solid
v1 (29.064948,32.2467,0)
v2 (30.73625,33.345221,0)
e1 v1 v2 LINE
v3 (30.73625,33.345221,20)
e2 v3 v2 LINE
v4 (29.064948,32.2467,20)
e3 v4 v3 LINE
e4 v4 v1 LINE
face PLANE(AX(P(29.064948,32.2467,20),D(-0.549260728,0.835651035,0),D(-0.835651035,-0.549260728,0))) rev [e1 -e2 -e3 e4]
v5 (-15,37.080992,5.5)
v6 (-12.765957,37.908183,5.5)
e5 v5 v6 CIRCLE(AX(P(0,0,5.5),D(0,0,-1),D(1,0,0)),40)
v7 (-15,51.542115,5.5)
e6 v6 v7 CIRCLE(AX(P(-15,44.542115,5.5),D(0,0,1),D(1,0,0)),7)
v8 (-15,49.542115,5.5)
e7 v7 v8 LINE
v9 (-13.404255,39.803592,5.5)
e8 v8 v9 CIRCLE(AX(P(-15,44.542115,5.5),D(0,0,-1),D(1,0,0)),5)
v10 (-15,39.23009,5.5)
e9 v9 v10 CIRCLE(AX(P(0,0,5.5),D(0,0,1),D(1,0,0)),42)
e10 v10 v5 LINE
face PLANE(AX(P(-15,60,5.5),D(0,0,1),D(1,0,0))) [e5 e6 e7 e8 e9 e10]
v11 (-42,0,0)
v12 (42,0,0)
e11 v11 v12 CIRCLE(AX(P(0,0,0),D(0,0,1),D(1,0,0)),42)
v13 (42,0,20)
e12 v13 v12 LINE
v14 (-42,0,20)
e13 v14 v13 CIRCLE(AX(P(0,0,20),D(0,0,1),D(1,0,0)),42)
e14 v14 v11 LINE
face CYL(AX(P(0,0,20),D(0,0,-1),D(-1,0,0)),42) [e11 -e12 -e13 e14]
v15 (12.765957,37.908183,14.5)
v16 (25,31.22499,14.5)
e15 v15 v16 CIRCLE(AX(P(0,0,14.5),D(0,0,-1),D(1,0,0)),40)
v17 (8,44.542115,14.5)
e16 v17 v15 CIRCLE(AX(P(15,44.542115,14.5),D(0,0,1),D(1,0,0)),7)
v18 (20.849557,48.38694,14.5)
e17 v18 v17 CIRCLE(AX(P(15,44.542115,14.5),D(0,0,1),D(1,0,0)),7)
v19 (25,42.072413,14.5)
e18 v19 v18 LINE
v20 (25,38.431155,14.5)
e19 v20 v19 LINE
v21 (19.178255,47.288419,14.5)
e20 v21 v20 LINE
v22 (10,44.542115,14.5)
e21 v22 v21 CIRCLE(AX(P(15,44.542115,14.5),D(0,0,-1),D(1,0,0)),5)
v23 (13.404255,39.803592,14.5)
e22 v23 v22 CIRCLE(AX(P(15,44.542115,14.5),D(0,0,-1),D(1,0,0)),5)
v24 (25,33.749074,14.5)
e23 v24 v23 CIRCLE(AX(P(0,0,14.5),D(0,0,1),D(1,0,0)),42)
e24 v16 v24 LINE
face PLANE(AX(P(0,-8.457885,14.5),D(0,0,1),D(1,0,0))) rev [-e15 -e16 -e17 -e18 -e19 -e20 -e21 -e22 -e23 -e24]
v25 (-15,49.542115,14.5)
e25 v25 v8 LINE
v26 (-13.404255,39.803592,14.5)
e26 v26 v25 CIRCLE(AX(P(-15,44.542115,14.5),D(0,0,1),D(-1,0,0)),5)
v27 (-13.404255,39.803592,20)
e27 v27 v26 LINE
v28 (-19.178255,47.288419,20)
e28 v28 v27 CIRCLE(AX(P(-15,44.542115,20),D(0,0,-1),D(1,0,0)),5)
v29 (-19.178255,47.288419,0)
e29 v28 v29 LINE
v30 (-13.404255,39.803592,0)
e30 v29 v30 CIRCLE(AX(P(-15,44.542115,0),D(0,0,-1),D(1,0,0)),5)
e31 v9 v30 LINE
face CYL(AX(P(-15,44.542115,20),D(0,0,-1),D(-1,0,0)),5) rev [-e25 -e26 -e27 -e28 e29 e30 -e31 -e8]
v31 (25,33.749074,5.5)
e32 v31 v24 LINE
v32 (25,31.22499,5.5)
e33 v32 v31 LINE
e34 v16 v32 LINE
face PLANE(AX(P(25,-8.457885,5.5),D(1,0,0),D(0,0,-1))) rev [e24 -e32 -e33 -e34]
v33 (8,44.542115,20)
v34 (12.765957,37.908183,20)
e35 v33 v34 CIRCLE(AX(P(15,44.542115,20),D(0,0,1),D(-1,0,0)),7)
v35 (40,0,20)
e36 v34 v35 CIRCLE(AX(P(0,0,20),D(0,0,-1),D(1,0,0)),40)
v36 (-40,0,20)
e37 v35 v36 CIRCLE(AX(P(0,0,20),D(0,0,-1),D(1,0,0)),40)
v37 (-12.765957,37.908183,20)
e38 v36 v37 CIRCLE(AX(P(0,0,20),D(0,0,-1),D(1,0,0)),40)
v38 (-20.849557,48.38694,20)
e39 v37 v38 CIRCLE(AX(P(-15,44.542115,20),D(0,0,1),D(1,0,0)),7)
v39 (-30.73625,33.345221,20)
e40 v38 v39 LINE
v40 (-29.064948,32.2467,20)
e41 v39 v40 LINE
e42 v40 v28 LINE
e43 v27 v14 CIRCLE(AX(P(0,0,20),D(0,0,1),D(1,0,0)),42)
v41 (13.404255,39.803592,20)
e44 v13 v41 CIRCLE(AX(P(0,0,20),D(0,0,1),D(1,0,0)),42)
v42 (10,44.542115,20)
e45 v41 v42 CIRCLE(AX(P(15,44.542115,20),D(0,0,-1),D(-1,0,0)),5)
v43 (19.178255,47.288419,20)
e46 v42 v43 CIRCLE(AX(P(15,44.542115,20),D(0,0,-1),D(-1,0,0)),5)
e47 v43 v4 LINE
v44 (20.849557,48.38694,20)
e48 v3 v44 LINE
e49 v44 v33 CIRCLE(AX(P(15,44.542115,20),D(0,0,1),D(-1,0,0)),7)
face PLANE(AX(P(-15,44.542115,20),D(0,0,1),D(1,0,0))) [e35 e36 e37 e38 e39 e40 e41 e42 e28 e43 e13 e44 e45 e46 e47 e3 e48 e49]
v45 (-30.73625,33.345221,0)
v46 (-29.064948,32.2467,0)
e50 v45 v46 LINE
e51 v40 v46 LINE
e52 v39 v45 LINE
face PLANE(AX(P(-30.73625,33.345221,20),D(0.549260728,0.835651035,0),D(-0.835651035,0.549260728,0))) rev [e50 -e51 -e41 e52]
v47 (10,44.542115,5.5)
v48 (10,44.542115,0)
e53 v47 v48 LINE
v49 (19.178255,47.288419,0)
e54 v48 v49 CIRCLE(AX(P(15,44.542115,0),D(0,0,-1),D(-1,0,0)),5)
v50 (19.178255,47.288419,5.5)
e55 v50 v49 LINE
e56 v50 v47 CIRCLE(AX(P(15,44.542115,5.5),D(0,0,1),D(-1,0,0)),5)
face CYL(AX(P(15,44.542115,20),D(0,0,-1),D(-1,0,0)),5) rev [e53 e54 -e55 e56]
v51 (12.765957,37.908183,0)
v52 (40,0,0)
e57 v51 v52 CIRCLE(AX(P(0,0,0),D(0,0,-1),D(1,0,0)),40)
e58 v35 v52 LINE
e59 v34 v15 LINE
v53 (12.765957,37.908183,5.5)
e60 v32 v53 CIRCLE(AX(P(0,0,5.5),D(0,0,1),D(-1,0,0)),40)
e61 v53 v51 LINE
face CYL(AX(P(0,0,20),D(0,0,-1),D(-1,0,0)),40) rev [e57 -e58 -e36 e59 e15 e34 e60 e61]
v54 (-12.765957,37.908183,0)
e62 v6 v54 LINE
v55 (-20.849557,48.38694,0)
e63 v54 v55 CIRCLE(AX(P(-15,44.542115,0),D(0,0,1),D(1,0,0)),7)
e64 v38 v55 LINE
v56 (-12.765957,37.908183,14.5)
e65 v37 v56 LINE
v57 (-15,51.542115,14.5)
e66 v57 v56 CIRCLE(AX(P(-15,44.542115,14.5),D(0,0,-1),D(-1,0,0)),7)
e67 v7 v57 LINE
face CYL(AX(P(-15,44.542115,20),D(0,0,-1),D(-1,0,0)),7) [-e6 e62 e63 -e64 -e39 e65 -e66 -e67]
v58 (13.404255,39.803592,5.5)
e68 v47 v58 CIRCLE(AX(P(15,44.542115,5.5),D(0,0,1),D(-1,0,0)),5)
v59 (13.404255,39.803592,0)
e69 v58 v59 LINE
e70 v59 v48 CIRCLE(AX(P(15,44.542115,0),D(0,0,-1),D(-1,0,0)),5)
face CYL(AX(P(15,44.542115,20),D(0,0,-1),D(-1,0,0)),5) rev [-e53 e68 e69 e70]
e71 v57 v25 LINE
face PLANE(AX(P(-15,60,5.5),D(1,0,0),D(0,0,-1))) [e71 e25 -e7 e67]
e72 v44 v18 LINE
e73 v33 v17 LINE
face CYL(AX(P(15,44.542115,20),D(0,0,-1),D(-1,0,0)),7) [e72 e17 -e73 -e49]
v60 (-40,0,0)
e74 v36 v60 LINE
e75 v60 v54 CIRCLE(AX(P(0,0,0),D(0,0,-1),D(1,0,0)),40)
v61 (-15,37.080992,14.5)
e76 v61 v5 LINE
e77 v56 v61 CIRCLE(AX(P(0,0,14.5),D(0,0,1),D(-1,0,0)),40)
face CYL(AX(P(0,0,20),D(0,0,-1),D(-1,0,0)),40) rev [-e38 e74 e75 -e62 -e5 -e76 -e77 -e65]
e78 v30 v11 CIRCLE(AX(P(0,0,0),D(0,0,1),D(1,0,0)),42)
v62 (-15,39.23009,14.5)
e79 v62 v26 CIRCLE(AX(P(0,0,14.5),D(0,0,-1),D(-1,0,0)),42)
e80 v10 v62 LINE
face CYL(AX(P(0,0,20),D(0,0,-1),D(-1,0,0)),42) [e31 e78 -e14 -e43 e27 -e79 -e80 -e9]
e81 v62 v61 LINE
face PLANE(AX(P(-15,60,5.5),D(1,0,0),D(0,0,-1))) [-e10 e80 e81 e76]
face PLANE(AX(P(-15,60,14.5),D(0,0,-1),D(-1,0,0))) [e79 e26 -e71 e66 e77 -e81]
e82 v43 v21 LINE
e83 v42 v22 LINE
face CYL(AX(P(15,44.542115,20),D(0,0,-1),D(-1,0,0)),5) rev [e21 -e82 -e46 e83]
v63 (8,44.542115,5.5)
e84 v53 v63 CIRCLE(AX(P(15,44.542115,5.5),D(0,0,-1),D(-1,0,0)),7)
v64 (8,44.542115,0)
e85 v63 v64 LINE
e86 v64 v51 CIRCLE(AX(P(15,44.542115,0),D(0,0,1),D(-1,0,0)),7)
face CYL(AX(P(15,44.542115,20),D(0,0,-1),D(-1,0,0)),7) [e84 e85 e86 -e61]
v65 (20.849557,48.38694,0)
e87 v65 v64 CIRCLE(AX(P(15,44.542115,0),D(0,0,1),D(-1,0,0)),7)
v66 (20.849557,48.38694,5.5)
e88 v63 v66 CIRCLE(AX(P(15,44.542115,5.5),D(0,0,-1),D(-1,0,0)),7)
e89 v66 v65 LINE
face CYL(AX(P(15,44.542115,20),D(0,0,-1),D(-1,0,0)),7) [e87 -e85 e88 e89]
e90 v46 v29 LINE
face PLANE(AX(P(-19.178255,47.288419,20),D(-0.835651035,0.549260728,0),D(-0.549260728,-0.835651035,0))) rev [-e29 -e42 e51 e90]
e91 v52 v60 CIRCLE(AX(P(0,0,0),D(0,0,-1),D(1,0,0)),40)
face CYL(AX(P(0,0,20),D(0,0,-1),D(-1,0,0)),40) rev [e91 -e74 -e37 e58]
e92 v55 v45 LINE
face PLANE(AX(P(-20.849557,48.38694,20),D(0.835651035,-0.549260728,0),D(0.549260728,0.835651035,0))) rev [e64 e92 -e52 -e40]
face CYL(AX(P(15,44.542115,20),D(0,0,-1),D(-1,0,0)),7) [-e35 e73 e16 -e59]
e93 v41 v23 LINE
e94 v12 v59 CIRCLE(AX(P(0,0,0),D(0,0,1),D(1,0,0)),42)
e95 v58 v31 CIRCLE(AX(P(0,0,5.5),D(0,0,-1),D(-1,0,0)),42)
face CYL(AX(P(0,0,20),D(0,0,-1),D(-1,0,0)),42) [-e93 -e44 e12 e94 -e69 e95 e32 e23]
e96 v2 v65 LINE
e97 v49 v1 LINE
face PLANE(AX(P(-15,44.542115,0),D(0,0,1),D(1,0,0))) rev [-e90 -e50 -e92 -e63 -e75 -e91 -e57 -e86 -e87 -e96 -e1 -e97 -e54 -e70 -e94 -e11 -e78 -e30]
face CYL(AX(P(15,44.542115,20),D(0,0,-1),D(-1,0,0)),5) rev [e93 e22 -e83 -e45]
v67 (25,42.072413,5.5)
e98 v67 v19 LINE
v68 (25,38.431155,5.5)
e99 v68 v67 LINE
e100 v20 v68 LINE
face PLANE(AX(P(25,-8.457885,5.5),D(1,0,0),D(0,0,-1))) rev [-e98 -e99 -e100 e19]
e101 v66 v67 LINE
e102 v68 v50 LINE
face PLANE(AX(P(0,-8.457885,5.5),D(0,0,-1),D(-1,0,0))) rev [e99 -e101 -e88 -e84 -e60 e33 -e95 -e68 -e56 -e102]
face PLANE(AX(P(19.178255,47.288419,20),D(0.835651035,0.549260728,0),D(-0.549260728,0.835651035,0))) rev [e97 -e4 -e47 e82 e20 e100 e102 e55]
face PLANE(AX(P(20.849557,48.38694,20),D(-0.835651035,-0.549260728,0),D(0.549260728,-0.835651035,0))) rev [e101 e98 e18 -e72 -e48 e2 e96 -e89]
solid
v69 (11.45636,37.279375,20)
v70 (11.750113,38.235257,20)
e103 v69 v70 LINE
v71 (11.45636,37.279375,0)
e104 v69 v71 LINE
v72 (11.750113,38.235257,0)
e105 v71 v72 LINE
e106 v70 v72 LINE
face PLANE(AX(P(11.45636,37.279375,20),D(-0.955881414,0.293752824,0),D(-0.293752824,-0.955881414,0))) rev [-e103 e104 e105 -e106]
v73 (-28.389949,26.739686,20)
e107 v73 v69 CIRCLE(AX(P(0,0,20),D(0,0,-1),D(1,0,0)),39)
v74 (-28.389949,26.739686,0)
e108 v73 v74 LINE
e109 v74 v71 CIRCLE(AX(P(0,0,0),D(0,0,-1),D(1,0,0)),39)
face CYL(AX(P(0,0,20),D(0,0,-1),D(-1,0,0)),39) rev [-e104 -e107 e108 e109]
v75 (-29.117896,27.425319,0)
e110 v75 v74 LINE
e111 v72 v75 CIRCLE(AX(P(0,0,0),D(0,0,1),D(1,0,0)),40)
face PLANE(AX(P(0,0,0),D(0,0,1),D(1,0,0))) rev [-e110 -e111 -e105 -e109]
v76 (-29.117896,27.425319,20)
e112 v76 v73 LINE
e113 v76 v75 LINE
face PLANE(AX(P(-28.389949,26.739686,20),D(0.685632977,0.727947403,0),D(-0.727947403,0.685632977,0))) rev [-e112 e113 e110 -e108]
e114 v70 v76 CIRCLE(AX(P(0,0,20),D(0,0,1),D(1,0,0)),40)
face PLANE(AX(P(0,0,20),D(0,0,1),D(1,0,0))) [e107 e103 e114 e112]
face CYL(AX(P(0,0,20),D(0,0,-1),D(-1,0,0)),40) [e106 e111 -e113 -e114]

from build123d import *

# Parameters (mm, degrees)
EXTRUDE_1_DEPTH     = 20
SKETCH_3_W          = 20
SKETCH_3_H          = 9
CUT_EXTRUDE_1_DEPTH = 60
SKETCH_4_W          = 25
SKETCH_4_H          = 9
CUT_EXTRUDE_2_DEPTH = 60
EXTRUDE_2_DEPTH     = 20


with BuildPart() as part:
    # 草图1 → 凸台-拉伸1 (new body)
    with BuildSketch(Plane.XY):
        with BuildLine():
            Line((19.178255175, 47.288418545), (29.064948286, 32.246699915))
            Line((29.064948286, 32.246699915), (30.736250356, 33.345221372))
            Line((30.736250356, 33.345221372), (20.849557245, 48.386940001))
            ThreePointArc((20.849557245, 48.386940001), (9.45752093, 48.81773483), (12.765957447, 37.908182896))
            ThreePointArc((12.765957447, 37.908182896), (0, -40), (-12.765957447, 37.908182896))
            ThreePointArc((-12.765957447, 37.908182896), (-9.45752093, 48.81773483), (-20.849557245, 48.386940001))
            Line((-20.849557245, 48.386940001), (-30.736250356, 33.345221372))
            Line((-30.736250356, 33.345221372), (-29.064948286, 32.246699915))
            Line((-29.064948286, 32.246699915), (-19.178255175, 47.288418545))
            ThreePointArc((-19.178255175, 47.288418545), (-11.041086379, 47.596129136), (-13.404255319, 39.803592041))
            ThreePointArc((-13.404255319, 39.803592041), (0, -42), (13.404255319, 39.803592041))
            ThreePointArc((13.404255319, 39.803592041), (11.041086379, 47.596129136), (19.178255175, 47.288418545))
        make_face()
    extrude(amount=EXTRUDE_1_DEPTH)

    # 草图3 → 切除-拉伸1 (cut)
    with BuildSketch(Plane(origin=(0, 0, 0), x_dir=(1, 0, 0), z_dir=(0, 1, 0))):
        with Locations((-5, -10)):
            Rectangle(SKETCH_3_W, SKETCH_3_H)
    extrude(amount=CUT_EXTRUDE_1_DEPTH, mode=Mode.SUBTRACT)

    # 草图4 → 切除-拉伸2 (cut)
    with BuildSketch(Plane(origin=(0, 51.542114903, 0), x_dir=(1, 0, 0), z_dir=(0, 1, 0))):
        with Locations((12.5, -10)):
            Rectangle(SKETCH_4_W, SKETCH_4_H)
    extrude(amount=-CUT_EXTRUDE_2_DEPTH, mode=Mode.SUBTRACT)


with BuildPart() as body_2:
    # 草图5 → 凸台-拉伸2 (new body)
    with BuildSketch(Plane.XY):
        with BuildLine():
            Line((-28.389948704, 26.739686097), (-29.117896107, 27.425319074))
            ThreePointArc((-29.117896107, 27.425319074), (-10.228570764, 38.6700962), (11.750112977, 38.235256571))
            Line((11.750112977, 38.235256571), (11.456360153, 37.279375156))
            ThreePointArc((11.456360153, 37.279375156), (-9.972856495, 37.703343795), (-28.389948704, 26.739686097))
        make_face()
    extrude(amount=EXTRUDE_2_DEPTH)


solid = Compound([part.part, body_2.part])
